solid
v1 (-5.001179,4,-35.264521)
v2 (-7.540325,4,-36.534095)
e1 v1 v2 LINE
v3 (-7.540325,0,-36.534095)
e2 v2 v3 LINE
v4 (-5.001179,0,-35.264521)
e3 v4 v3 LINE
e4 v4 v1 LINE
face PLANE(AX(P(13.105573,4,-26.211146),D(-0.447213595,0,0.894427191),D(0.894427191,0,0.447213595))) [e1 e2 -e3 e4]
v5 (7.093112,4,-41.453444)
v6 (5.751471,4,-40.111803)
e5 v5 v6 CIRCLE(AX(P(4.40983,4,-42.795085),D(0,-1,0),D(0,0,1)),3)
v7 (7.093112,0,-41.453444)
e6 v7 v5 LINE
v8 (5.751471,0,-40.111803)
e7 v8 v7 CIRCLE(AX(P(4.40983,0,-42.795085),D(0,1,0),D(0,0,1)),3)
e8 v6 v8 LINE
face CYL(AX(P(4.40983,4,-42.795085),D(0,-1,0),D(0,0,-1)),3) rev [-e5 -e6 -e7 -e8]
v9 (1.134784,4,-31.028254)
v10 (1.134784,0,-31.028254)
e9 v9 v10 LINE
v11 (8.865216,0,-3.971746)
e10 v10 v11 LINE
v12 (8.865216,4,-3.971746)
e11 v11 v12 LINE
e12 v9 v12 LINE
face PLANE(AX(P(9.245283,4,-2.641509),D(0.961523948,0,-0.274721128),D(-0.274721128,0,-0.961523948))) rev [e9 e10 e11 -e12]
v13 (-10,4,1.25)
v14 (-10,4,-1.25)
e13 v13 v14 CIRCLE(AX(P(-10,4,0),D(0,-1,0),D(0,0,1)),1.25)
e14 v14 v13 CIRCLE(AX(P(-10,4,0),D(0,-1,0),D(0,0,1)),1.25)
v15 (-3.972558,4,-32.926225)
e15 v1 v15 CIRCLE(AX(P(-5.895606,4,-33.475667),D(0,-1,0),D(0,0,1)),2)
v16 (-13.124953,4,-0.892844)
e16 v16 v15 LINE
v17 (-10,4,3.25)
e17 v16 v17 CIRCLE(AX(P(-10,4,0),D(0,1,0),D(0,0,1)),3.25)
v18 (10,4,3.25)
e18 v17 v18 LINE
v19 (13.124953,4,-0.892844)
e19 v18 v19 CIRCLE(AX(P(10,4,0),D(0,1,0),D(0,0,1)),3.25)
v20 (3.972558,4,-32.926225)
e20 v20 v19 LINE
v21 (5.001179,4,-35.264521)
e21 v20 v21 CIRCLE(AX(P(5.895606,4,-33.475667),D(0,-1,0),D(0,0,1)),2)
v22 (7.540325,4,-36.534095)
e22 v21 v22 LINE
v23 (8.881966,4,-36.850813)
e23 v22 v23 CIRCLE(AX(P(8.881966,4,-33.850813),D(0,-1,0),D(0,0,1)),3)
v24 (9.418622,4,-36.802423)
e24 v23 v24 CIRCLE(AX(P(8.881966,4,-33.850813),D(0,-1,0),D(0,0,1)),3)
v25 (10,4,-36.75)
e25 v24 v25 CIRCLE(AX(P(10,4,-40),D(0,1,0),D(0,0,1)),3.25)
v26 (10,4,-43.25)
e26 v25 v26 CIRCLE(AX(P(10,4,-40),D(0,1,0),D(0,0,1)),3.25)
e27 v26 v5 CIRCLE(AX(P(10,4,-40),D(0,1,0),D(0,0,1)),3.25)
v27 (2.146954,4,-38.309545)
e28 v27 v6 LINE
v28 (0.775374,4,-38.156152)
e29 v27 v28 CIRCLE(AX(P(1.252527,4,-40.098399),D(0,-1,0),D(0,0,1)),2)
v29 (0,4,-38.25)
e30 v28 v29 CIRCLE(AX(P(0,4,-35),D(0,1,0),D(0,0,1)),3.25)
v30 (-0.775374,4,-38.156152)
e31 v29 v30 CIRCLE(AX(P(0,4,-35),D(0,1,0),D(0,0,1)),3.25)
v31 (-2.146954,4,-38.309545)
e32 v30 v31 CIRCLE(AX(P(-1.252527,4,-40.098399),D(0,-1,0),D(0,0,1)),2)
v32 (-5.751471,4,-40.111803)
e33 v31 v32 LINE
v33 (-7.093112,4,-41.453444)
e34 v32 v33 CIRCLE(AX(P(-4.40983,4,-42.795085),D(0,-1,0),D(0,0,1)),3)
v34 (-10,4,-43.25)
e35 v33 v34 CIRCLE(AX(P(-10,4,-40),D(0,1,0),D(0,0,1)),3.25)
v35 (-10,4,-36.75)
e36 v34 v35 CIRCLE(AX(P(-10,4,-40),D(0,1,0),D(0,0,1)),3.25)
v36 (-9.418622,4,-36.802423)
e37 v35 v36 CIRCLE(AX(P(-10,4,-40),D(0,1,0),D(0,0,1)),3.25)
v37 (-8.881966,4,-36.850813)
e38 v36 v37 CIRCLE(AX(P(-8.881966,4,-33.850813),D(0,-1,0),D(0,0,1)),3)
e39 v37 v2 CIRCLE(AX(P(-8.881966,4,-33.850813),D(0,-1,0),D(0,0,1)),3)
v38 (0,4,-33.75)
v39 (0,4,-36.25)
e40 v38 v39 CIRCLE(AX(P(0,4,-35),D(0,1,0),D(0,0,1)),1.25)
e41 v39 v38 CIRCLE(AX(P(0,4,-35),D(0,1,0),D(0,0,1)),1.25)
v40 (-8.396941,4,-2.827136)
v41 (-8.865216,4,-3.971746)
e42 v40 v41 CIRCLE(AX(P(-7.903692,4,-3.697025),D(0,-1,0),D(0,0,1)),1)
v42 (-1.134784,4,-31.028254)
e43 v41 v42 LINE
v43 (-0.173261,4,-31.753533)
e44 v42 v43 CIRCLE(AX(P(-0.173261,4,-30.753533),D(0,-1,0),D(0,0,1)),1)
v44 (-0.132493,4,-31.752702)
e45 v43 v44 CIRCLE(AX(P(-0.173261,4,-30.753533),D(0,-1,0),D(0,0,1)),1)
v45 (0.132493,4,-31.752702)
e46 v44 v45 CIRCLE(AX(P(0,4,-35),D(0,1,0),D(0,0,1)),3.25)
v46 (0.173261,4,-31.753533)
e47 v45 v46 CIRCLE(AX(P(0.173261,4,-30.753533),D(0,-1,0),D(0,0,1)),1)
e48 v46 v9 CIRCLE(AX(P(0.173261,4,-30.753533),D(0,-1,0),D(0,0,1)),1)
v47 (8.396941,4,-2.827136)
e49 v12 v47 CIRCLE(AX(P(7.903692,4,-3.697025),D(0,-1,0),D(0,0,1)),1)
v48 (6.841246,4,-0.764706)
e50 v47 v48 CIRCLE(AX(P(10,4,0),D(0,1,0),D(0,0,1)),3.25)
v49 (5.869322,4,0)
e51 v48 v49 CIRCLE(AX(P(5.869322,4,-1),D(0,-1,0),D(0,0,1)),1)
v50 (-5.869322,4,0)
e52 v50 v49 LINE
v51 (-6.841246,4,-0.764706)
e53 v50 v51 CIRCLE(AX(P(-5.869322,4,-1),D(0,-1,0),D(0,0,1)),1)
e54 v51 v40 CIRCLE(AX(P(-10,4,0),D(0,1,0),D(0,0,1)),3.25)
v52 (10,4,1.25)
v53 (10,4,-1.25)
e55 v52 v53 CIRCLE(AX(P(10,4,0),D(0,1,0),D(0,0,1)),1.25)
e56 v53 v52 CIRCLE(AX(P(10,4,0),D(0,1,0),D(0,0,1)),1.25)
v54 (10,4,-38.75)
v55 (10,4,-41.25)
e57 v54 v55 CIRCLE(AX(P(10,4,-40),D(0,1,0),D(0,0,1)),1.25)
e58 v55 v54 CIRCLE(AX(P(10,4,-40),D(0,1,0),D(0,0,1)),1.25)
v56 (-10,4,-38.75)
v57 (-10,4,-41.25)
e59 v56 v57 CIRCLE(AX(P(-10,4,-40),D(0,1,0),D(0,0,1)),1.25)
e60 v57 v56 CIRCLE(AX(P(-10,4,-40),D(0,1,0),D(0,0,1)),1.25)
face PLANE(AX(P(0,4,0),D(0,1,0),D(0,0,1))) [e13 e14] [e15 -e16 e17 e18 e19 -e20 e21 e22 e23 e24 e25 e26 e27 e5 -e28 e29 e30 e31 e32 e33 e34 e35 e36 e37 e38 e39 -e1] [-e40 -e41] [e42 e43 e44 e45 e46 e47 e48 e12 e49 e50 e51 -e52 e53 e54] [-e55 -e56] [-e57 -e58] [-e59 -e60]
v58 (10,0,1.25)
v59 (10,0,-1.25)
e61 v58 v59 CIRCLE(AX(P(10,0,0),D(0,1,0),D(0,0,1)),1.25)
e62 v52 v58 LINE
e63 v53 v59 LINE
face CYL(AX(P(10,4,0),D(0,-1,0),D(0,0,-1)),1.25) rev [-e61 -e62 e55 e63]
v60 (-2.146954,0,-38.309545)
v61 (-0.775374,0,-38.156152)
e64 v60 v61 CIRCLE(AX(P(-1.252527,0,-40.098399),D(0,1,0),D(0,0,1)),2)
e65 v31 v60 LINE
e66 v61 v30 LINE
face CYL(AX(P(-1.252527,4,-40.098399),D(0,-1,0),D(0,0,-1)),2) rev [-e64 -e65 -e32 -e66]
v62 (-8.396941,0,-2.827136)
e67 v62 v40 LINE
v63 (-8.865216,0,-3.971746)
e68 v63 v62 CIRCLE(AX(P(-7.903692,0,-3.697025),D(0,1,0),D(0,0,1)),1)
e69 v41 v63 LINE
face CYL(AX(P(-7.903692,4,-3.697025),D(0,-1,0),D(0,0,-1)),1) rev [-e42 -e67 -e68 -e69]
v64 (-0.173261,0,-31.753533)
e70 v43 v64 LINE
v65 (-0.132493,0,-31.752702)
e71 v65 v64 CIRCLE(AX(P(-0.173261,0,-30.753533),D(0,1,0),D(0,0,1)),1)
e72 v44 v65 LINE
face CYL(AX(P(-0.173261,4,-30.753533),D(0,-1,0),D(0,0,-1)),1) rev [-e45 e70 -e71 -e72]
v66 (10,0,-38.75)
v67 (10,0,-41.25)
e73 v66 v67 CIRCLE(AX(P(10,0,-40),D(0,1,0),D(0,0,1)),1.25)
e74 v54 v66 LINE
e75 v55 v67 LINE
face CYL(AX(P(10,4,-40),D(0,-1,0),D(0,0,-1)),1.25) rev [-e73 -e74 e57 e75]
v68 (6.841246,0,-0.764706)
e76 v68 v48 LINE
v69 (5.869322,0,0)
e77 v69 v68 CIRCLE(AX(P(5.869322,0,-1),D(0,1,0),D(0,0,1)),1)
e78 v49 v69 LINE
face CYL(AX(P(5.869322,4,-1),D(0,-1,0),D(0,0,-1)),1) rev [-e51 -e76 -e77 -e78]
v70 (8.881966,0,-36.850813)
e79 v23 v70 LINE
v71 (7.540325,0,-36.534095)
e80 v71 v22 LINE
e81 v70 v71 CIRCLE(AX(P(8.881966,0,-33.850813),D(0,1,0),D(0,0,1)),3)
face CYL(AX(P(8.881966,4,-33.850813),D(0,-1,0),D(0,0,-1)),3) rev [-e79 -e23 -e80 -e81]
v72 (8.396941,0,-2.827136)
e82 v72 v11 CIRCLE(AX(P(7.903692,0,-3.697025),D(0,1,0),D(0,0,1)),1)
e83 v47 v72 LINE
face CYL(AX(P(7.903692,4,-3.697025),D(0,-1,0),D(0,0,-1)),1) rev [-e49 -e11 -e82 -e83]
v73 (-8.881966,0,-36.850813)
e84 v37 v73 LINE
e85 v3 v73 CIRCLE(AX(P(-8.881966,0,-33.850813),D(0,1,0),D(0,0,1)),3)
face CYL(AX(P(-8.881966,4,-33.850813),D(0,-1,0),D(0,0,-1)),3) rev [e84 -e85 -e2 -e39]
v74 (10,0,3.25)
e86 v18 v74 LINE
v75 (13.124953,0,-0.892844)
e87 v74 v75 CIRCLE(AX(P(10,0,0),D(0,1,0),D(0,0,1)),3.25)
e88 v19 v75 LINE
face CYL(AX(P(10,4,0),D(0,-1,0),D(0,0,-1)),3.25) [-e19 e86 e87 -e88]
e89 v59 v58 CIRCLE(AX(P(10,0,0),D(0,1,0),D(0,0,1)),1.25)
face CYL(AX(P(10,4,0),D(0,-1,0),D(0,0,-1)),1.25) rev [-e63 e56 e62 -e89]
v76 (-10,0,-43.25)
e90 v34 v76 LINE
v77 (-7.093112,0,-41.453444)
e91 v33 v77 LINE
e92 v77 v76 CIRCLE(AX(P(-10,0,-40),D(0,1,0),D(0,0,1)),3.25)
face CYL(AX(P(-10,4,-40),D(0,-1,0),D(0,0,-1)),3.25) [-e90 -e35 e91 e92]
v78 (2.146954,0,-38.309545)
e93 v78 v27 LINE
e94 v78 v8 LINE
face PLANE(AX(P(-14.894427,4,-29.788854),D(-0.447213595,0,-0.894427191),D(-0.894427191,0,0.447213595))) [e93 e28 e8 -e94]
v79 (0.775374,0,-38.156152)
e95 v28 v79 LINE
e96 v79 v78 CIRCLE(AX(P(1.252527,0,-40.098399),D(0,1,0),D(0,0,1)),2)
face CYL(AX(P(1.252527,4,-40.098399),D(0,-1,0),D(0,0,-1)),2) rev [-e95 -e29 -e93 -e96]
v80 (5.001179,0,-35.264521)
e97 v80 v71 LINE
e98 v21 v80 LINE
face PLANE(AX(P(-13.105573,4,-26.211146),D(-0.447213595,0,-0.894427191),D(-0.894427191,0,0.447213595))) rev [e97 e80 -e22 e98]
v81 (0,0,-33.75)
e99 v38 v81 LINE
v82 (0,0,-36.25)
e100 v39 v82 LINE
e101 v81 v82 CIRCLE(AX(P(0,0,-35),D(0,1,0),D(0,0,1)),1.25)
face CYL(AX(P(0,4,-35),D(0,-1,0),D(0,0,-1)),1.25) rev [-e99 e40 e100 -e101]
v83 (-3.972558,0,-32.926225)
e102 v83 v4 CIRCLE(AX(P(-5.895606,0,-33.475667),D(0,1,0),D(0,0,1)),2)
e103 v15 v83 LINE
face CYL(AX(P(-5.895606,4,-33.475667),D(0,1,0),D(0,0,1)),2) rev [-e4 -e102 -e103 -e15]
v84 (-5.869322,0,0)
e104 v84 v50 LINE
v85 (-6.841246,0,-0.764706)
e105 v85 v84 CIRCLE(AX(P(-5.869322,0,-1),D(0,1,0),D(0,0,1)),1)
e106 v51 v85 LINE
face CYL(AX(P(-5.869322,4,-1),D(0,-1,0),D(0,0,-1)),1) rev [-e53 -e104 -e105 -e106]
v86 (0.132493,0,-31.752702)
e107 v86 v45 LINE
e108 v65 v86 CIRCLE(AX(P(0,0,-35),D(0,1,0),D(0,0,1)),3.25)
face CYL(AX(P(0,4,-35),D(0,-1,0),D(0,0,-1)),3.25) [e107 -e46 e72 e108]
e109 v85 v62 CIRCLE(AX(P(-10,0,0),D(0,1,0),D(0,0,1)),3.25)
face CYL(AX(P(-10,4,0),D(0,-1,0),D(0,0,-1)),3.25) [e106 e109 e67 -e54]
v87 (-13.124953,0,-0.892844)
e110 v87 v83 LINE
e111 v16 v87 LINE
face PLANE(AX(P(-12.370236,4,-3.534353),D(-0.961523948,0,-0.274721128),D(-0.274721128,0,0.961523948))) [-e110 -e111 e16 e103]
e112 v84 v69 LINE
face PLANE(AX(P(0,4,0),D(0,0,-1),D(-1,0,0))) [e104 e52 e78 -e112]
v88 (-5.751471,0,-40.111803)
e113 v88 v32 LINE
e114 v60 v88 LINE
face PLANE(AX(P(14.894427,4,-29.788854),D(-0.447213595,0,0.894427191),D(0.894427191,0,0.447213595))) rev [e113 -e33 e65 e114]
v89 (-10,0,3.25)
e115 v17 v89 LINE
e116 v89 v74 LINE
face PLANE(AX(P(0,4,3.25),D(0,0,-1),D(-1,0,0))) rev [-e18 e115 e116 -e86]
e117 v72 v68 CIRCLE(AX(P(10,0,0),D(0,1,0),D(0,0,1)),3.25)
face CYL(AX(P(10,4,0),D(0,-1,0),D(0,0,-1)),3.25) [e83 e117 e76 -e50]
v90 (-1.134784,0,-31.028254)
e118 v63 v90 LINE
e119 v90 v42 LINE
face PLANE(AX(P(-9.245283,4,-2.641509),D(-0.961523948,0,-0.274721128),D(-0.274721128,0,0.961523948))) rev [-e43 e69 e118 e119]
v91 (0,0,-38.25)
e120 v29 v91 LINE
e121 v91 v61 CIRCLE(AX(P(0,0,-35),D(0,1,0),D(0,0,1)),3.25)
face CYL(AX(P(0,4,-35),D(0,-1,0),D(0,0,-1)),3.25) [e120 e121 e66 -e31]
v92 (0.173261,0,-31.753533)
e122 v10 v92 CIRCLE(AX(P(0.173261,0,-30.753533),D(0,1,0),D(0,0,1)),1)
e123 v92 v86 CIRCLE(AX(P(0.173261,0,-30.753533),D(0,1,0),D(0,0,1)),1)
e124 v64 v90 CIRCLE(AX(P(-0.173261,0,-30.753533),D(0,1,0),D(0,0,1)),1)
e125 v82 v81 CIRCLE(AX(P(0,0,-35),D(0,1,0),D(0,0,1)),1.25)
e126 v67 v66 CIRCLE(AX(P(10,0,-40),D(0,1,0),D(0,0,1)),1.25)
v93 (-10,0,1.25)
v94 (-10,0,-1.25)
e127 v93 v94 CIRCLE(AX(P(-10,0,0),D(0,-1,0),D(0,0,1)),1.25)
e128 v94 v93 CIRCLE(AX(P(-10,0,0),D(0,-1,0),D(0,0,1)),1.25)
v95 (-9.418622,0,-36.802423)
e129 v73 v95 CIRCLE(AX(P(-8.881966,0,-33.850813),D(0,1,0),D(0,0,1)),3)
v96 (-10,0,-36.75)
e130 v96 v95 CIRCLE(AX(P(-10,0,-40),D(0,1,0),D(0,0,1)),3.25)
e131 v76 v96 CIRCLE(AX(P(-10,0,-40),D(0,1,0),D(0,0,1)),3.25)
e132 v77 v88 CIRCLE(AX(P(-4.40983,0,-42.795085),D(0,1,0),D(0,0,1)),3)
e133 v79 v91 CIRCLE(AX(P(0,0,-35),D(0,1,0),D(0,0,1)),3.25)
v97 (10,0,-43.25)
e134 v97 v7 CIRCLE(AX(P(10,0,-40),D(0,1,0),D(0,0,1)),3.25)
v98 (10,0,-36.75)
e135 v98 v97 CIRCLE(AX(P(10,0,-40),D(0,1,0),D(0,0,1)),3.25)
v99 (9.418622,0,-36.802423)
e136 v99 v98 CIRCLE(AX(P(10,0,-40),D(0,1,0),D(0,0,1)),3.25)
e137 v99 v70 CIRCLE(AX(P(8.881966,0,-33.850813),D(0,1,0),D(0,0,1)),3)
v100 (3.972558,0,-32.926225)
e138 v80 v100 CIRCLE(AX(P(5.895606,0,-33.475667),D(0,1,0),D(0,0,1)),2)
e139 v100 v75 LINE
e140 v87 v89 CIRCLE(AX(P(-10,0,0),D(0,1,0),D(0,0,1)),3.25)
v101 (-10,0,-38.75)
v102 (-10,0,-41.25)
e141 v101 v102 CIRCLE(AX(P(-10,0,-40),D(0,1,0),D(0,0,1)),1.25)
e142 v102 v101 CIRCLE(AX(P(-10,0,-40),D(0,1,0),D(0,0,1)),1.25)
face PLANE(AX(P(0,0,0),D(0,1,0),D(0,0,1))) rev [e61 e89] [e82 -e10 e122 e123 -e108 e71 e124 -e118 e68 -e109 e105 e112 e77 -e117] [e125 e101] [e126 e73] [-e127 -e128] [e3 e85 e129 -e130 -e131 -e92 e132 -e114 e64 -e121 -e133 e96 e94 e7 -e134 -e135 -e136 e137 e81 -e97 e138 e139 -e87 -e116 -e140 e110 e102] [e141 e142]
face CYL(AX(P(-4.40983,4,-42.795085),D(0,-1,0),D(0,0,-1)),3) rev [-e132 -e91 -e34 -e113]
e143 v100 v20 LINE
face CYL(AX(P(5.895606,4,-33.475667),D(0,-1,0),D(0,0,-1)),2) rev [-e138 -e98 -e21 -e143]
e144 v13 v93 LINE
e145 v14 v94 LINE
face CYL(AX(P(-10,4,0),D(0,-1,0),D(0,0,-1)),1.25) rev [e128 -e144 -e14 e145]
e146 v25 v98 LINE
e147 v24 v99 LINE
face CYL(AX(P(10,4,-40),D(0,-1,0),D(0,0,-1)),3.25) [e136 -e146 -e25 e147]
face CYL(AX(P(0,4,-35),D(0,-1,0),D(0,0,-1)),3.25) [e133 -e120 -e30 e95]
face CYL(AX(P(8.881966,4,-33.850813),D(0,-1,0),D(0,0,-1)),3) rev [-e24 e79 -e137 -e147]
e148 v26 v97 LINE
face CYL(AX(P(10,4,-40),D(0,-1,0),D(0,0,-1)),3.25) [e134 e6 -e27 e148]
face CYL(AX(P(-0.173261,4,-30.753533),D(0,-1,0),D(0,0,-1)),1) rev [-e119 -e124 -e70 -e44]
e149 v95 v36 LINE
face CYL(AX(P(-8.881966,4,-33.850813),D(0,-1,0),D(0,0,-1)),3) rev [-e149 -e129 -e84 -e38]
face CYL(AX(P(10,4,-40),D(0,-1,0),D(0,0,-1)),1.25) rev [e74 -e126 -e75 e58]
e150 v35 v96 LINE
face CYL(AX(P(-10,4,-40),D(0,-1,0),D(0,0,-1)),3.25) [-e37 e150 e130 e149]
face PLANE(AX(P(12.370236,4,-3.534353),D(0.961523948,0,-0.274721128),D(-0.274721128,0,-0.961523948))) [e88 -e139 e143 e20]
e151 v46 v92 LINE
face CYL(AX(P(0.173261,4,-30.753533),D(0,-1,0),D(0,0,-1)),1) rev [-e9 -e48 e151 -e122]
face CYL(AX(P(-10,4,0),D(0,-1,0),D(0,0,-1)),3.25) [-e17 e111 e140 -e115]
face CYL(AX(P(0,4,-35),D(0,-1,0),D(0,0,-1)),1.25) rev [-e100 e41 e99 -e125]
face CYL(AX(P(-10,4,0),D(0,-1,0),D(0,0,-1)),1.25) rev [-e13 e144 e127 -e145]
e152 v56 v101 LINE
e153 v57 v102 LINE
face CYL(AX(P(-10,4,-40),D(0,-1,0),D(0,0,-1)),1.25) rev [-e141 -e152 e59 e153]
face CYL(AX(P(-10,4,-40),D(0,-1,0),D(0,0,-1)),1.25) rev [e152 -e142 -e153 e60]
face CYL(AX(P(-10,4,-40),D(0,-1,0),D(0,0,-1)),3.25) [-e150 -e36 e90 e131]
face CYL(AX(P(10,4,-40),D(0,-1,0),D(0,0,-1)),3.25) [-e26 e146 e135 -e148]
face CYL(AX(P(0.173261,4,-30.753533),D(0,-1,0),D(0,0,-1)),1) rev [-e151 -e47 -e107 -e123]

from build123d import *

# Parameters (mm, degrees)
SKETCH_1_R      = 3.25
SKETCH_1_R_2    = 1.25
EXTRUDE_1_DEPTH = 4
FILLET_1_R      = 1
FILLET_2_R      = 2
FILLET_3_R      = 3


with BuildPart() as part:
    # 草图1 → 凸台-拉伸1 (new body)
    # profile 1 of 12: a face of its own
    with BuildSketch(Plane(origin=(0, 0, 0), x_dir=(1, 0, 0), z_dir=(0, 1, 0))):
        with Locations((-10, 40)):
            Circle(SKETCH_1_R)
        with Locations(Location((-10, 40, 0), (0, 0, 270))):
            Circle(SKETCH_1_R_2, mode=Mode.SUBTRACT)
    # profile 2 of 12: a face of its own
    with BuildSketch(Plane(origin=(0, 0, 0), x_dir=(1, 0, 0), z_dir=(0, 1, 0))):
        with BuildLine():
            Line((-8.603139344, 37.065501694), (-3.516561637, 34.522212841))
            Line((-3.516561637, 34.522212841), (-3.12495283, 35.892843666))
            ThreePointArc((-3.12495283, 35.892843666), (-2.480682914, 37.099693378), (-1.396860656, 37.934498306))
            Line((-1.396860656, 37.934498306), (-6.814284962, 40.643210458))
            ThreePointArc((-6.814284962, 40.643210458), (-6.766111174, 40.32320746), (-6.75, 40))
            ThreePointArc((-6.75, 40), (-7.252064672, 38.26467541), (-8.603139344, 37.065501694))
        make_face()
    # profile 3 of 12: a face of its own
    with BuildSketch(Plane(origin=(0, 0, 0), x_dir=(1, 0, 0), z_dir=(0, 1, 0))):
        with BuildLine():
            ThreePointArc((-13.12495283, 0.892843666), (-11.578339526, 2.841011147), (-9.107156334, 3.12495283))
            Line((-9.107156334, 3.12495283), (-0.892843666, 31.87504717))
            ThreePointArc((-0.892843666, 31.87504717), (-2.38713669, 32.79453442), (-3.185715038, 34.356789542))
            Line((-3.185715038, 34.356789542), (-3.516561637, 34.522212841))
            Line((-3.516561637, 34.522212841), (-13.12495283, 0.892843666))
        make_face()
    # profile 4 of 12: a face of its own
    with BuildSketch(Plane(origin=(0, 0, 0), x_dir=(1, 0, 0), z_dir=(0, 1, 0))):
        with BuildLine():
            ThreePointArc((3.185715038, 34.356789542), (2.38713669, 32.79453442), (0.892843666, 31.87504717))
            Line((0.892843666, 31.87504717), (9.107156334, 3.12495283))
            ThreePointArc((9.107156334, 3.12495283), (11.578339526, 2.841011147), (13.12495283, 0.892843666))
            Line((13.12495283, 0.892843666), (3.516561637, 34.522212841))
            Line((3.516561637, 34.522212841), (3.185715038, 34.356789542))
        make_face()
    # profile 5 of 12: a face of its own
    with BuildSketch(Plane(origin=(0, 0, 0), x_dir=(1, 0, 0), z_dir=(0, 1, 0))):
        with Locations((-10, 0)):
            Circle(SKETCH_1_R)
        with Locations(Location((-10, 0, 0), (0, 0, 270))):
            Circle(SKETCH_1_R_2, mode=Mode.SUBTRACT)
    # profile 6 of 12: a face of its own
    with BuildSketch(Plane(origin=(0, 0, 0), x_dir=(1, 0, 0), z_dir=(0, 1, 0))):
        with BuildLine():
            Line((6.75, 0), (-6.75, 0))
            ThreePointArc((-6.75, 0), (-7.701902961, -2.298097039), (-10, -3.25))
            Line((-10, -3.25), (10, -3.25))
            ThreePointArc((10, -3.25), (7.701902961, -2.298097039), (6.75, 0))
        make_face()
    # profile 7 of 12: a face of its own
    with BuildSketch(Plane(origin=(0, 0, 0), x_dir=(1, 0, 0), z_dir=(0, 1, 0))):
        with Locations((10, 0)):
            Circle(SKETCH_1_R)
        with Locations(Location((10, 0, 0), (0, 0, 270))):
            Circle(SKETCH_1_R_2, mode=Mode.SUBTRACT)
    # profile 8 of 12: a face of its own
    with BuildSketch(Plane(origin=(0, 0, 0), x_dir=(1, 0, 0), z_dir=(0, 1, 0))):
        with Locations((0, 35)):
            Circle(SKETCH_1_R)
        with Locations(Location((0, 35, 0), (0, 0, 270))):
            Circle(SKETCH_1_R_2, mode=Mode.SUBTRACT)
    # profile 9 of 12: a face of its own
    with BuildSketch(Plane(origin=(0, 0, 0), x_dir=(1, 0, 0), z_dir=(0, 1, 0))):
        with BuildLine():
            Line((-3.516561637, 34.522212841), (-3.185715038, 34.356789542))
            ThreePointArc((-3.185715038, 34.356789542), (-3.247460208, 35.128460874), (-3.12495283, 35.892843666))
            Line((-3.12495283, 35.892843666), (-3.516561637, 34.522212841))
        make_face()
    # profile 10 of 12: a face of its own
    with BuildSketch(Plane(origin=(0, 0, 0), x_dir=(1, 0, 0), z_dir=(0, 1, 0))):
        with BuildLine():
            ThreePointArc((3.25, 35), (3.233888826, 34.67679254), (3.185715038, 34.356789542))
            Line((3.185715038, 34.356789542), (3.516561637, 34.522212841))
            Line((3.516561637, 34.522212841), (3.12495283, 35.892843666))
            ThreePointArc((3.12495283, 35.892843666), (3.21858639, 35.450778939), (3.25, 35))
        make_face()
    # profile 11 of 12: a face of its own
    with BuildSketch(Plane(origin=(0, 0, 0), x_dir=(1, 0, 0), z_dir=(0, 1, 0))):
        with BuildLine():
            Line((3.12495283, 35.892843666), (3.516561637, 34.522212841))
            Line((3.516561637, 34.522212841), (8.603139344, 37.065501694))
            ThreePointArc((8.603139344, 37.065501694), (7.093111629, 38.546555815), (6.814284962, 40.643210458))
            Line((6.814284962, 40.643210458), (1.396860656, 37.934498306))
            ThreePointArc((1.396860656, 37.934498306), (2.480682914, 37.099693378), (3.12495283, 35.892843666))
        make_face()
    # profile 12 of 12: a face of its own
    with BuildSketch(Plane(origin=(0, 0, 0), x_dir=(1, 0, 0), z_dir=(0, 1, 0))):
        with Locations((10, 40)):
            Circle(SKETCH_1_R)
        with Locations(Location((10, 40, 0), (0, 0, 270))):
            Circle(SKETCH_1_R_2, mode=Mode.SUBTRACT)
    extrude(amount=EXTRUDE_1_DEPTH)

    # 圆角1
    fillet_1_edges = [part.edges().sort_by_distance(p)[0] for p in [
        (9.107156334, 2, -3.12495283),
        (0.892843666, 2, -31.87504717),
        (-0.892843666, 2, -31.87504717),
        (-9.107156334, 2, -3.12495283),
        (-6.75, 2, 0),
        (6.75, 2, 0),
    ]]
    fillet(fillet_1_edges, radius=FILLET_1_R)

    # 圆角2
    fillet_2_edges = [part.edges().sort_by_distance(p)[0] for p in [
        (-3.516561637, 2, -34.522212841),
        (-1.396860656, 2, -37.934498306),
        (1.396860656, 2, -37.934498306),
        (3.516561637, 2, -34.522212841),
    ]]
    fillet(fillet_2_edges, radius=FILLET_2_R)

    # 圆角3
    fillet_3_edges = [part.edges().sort_by_distance(p)[0] for p in [
        (-8.603139344, 2, -37.065501694),
        (-6.814284962, 2, -40.643210458),
        (6.814284962, 2, -40.643210458),
        (8.603139344, 2, -37.065501694),
    ]]
    fillet(fillet_3_edges, radius=FILLET_3_R)


solid = part.part
